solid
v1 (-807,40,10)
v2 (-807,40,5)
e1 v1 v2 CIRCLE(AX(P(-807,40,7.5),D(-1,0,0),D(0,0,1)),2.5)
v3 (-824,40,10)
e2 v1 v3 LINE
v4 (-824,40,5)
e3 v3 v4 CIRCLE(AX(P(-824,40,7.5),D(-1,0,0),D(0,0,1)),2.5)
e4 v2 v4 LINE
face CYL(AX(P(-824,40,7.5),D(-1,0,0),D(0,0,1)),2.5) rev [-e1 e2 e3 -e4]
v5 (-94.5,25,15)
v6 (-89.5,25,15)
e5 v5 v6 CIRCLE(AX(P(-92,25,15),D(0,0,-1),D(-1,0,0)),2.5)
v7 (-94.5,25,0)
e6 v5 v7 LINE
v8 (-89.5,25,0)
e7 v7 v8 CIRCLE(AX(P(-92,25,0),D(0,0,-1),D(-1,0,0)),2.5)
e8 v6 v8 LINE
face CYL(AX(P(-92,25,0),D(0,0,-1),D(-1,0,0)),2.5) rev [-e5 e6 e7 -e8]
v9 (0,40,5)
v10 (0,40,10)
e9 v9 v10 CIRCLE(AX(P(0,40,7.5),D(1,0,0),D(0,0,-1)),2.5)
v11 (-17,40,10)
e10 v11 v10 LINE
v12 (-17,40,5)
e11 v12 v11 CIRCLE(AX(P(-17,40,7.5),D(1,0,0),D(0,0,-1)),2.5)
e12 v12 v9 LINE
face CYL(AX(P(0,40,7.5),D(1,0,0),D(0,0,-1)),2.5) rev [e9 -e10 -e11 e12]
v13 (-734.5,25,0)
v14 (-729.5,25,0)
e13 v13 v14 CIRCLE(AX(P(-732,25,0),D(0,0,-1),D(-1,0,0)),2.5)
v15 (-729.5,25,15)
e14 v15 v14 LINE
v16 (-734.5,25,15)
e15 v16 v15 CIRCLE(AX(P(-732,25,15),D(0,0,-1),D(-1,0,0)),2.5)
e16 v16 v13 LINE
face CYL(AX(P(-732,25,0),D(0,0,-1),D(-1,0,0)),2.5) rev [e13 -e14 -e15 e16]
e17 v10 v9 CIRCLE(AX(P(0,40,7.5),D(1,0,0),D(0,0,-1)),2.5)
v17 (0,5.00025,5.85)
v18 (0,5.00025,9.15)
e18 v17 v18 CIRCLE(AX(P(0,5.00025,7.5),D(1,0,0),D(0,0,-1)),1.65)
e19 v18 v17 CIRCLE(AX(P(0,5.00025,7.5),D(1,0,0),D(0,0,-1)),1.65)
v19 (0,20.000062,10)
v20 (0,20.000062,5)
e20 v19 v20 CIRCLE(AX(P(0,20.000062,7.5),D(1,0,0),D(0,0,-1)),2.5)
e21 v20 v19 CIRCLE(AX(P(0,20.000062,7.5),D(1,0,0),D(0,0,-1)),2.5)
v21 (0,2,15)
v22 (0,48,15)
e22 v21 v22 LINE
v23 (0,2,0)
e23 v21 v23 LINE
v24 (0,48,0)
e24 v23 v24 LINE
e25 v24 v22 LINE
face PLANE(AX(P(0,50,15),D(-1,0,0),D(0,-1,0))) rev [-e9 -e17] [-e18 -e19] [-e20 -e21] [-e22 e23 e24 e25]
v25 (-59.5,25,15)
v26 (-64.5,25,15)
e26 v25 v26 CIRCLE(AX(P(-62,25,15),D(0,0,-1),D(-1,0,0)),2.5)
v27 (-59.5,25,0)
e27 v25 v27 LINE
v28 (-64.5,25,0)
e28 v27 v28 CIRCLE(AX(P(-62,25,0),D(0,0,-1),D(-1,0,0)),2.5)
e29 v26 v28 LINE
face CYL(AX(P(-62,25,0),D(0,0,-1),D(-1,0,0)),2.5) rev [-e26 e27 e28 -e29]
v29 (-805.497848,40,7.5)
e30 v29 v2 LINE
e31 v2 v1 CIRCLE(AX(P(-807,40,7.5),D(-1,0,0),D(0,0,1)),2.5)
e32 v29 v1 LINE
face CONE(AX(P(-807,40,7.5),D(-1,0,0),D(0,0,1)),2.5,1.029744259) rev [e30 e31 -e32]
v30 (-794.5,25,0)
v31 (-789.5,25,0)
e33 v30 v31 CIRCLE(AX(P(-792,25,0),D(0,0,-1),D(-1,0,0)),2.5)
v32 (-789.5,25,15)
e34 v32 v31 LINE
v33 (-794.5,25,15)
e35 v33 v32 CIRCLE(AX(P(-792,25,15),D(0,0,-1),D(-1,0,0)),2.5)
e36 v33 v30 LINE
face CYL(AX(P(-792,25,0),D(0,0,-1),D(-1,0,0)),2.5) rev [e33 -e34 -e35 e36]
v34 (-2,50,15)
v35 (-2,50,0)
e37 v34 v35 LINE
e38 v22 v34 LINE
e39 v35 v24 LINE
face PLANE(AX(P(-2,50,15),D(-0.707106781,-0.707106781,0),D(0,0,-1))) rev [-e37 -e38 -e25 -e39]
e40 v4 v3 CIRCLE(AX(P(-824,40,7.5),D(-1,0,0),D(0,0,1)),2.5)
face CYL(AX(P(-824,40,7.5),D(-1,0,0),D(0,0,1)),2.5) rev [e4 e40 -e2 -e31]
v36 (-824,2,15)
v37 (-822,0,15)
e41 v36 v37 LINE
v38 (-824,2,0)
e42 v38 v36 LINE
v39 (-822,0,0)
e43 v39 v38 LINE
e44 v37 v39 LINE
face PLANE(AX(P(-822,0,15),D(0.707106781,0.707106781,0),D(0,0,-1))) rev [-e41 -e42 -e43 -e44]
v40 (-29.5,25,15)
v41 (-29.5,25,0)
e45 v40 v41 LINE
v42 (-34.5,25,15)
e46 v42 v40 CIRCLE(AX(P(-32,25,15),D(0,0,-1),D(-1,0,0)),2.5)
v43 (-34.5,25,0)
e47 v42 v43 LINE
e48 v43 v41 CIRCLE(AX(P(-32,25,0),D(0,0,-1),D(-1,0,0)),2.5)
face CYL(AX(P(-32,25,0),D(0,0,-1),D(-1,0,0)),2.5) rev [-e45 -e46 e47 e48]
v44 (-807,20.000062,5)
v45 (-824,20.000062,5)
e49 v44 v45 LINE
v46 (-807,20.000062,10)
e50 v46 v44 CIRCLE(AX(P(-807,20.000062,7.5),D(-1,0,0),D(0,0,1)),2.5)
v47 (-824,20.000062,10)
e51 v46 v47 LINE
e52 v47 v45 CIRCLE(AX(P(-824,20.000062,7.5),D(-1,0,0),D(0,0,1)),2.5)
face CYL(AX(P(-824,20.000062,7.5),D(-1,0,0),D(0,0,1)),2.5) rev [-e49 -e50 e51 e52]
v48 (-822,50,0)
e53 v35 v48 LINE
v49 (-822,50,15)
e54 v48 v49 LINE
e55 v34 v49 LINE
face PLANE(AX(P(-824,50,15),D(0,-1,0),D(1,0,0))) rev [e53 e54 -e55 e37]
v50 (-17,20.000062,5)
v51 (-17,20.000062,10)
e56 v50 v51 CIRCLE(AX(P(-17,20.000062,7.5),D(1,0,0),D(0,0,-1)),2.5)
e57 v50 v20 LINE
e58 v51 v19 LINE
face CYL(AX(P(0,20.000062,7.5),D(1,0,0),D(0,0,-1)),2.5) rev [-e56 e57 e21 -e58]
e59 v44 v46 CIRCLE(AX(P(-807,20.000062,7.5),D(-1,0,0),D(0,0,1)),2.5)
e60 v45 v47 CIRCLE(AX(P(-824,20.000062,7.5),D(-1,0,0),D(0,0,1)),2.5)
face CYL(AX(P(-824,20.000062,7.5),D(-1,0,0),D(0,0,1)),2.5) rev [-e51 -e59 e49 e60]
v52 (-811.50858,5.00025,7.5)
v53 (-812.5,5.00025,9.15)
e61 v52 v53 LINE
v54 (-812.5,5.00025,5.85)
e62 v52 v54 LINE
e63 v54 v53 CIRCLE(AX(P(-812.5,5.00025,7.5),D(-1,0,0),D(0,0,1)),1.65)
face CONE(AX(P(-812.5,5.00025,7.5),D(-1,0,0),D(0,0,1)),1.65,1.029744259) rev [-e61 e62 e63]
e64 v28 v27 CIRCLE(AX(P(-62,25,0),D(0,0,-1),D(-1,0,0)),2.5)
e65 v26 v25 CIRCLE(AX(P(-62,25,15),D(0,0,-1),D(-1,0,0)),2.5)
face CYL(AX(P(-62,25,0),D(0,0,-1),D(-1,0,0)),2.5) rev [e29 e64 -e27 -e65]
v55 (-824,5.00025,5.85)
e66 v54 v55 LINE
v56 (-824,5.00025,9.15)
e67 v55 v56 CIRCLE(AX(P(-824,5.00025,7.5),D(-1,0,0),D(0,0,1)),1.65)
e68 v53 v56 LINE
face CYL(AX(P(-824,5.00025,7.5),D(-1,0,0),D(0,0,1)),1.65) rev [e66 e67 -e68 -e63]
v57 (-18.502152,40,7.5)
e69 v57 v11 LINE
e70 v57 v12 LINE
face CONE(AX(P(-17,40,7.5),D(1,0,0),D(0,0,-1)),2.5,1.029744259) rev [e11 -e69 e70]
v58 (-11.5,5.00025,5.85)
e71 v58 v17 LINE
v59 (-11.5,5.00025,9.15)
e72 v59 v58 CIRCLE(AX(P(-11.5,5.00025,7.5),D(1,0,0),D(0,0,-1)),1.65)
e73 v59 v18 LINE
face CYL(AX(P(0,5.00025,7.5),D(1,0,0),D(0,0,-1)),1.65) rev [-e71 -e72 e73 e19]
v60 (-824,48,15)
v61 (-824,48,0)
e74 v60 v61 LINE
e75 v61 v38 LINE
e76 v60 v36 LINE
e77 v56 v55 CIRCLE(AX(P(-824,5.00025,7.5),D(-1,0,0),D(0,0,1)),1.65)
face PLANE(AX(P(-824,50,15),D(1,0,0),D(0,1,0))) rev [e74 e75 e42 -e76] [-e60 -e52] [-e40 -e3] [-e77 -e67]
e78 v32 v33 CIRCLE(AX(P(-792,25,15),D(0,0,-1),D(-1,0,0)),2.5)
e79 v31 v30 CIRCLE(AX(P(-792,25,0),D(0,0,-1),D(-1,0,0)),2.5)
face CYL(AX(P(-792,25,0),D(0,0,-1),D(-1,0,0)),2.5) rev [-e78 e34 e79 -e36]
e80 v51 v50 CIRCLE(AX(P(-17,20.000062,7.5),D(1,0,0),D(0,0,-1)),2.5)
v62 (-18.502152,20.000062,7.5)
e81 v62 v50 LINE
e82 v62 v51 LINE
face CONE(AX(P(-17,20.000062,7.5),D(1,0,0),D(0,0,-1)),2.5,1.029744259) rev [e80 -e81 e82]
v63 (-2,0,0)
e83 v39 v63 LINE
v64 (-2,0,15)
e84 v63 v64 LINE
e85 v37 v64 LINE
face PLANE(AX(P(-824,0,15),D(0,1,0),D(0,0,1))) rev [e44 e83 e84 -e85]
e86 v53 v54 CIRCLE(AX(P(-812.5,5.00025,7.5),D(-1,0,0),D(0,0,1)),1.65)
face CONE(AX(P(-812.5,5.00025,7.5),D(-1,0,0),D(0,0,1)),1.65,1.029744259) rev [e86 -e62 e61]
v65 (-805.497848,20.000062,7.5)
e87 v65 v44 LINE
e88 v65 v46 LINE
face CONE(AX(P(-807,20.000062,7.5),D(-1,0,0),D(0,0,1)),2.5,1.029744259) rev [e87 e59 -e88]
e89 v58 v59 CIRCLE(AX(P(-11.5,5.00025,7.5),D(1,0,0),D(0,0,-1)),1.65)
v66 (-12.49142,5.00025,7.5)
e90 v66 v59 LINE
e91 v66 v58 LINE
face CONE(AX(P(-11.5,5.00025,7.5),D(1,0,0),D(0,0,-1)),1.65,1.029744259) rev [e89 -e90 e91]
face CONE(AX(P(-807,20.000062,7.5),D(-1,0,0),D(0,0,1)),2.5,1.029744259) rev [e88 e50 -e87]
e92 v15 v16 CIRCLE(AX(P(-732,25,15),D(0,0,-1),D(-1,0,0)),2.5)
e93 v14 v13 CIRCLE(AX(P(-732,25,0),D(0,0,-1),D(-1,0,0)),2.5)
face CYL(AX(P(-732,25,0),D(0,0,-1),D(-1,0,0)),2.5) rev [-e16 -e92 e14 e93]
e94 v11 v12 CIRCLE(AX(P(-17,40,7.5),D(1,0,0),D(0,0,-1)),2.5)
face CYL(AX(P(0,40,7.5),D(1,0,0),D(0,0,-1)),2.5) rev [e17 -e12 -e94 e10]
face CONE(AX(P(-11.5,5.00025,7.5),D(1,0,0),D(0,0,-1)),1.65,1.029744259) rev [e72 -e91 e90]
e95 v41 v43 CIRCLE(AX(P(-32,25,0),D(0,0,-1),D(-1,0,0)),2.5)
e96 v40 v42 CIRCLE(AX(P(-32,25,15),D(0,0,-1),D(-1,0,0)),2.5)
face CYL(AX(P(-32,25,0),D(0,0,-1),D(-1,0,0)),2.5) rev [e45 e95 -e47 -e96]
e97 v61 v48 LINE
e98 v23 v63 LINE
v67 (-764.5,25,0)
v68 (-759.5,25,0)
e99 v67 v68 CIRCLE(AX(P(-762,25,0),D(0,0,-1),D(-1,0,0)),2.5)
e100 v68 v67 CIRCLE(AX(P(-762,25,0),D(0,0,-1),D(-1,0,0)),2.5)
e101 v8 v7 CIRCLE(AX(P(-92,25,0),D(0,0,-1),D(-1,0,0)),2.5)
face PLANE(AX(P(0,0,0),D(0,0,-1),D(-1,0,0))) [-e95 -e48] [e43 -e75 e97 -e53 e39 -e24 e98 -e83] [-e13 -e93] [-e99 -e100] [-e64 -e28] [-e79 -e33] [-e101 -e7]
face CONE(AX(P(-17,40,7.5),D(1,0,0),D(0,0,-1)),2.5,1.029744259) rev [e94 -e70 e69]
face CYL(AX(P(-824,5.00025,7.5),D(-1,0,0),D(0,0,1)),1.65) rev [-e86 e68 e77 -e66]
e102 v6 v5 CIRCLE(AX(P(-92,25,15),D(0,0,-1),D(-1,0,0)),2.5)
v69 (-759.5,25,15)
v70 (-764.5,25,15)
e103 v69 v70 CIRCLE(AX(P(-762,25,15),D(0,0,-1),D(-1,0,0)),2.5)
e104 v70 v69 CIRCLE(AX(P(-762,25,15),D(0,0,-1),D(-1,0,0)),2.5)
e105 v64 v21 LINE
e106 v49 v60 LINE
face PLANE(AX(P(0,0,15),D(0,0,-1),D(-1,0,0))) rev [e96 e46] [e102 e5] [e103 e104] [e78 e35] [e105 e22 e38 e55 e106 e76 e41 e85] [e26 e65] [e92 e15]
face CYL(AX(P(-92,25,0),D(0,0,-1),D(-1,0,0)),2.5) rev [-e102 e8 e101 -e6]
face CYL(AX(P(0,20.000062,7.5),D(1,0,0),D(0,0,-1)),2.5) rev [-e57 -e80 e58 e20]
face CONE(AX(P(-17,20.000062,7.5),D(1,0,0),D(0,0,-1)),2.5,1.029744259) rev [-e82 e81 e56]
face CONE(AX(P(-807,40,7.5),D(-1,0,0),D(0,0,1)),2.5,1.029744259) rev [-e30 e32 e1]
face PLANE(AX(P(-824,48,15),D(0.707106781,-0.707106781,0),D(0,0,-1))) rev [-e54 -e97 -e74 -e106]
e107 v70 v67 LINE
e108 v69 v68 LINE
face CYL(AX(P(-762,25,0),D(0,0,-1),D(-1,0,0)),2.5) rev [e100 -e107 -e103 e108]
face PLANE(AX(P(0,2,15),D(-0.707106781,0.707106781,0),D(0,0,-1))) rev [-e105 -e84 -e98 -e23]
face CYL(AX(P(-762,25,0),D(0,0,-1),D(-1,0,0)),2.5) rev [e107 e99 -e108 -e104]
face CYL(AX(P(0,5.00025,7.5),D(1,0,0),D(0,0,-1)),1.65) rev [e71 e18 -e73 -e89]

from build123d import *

# Parameters (mm, degrees)
SKETCH_1_W                  = 824
SKETCH_1_H                  = 50
EXTRUDE_1_DEPTH             = 15
HOLE_WIZARD_M6_1_AT_2_COUNT = 2
HOLE_WIZARD_M6_1_AT_2_PITCH = 19.9999375
HOLE_WIZARD_M6_2_D          = 5
HOLE_WIZARD_M6_2_DEPTH      = 17
HOLE_WIZARD_M6_2_TIP        = 1.502151548
CHAMFER_1_SIZE              = 2


with BuildPart() as part:
    # 草图1 → 凸台-拉伸1 (new body)
    with BuildSketch(Plane.XY):
        with Locations((-412, 25)):
            Rectangle(SKETCH_1_W, SKETCH_1_H)
    extrude(amount=EXTRUDE_1_DEPTH)

    # 草图3 → M6 螺纹孔1 (revolve, cut)
    with BuildSketch(Plane(origin=(0, 40, 7.5), x_dir=(0, 0, -1), z_dir=(0, 1, 0))):
        Polygon((0, 0), (0, 18.502151548), (2.5, 17), (2.5, 0), align=None)
    hole_wizard_m6_1 = revolve(axis=Axis((6.35, 40, 7.5), (-1, 0, 0)), mode=Mode.SUBTRACT)

    # M6 螺纹孔1 at 2: M6 螺纹孔1 ×2
    with Locations(*[(0, -i * HOLE_WIZARD_M6_1_AT_2_PITCH, 0) for i in range(1, HOLE_WIZARD_M6_1_AT_2_COUNT)]):
        add(hole_wizard_m6_1, mode=Mode.SUBTRACT)

    # 草图5 → M4 螺纹孔1 (revolve, cut)
    with BuildSketch(Plane(origin=(0, 5.000249994, 7.5), x_dir=(0, 0, -1), z_dir=(0, 1, 0))):
        Polygon((0, 0), (0, 12.491420021), (1.65, 11.5), (1.65, 0), align=None)
    hole_wizard_m4_1 = revolve(axis=Axis((6.35, 5.000249994, 7.5), (-1, 0, 0)), mode=Mode.SUBTRACT)

    # 镜向1: M6 螺纹孔1, M4 螺纹孔1 across plane
    add(hole_wizard_m6_1.mirror(Plane(origin=(-412, 0, 0), x_dir=(0, 0, 1), z_dir=(1, 0, 0))), mode=Mode.SUBTRACT)
    add(hole_wizard_m4_1.mirror(Plane(origin=(-412, 0, 0), x_dir=(0, 0, 1), z_dir=(1, 0, 0))), mode=Mode.SUBTRACT)

    # 镜向1 copy 1 sketch → 镜向1 copy 1 (revolve, cut)
    with BuildSketch(Plane(origin=(-824, 20.0000625, 7.5), x_dir=(0, 0, -1), z_dir=(0, 1, 0))):
        Polygon((0, 0), (0, -18.502151548), (2.5, -17), (2.5, 0), align=None)
    revolve(axis=Axis((-830.35, 20.0000625, 7.5), (-1, 0, 0)), mode=Mode.SUBTRACT)

    # M6 螺纹孔2
    with Locations(Plane(origin=(0, 0, 0), x_dir=(-1, 0, 0), z_dir=(0, 0, -1))):
        with Locations((792, 25), (32, 25), (62, 25), (92, 25), (732, 25), (762, 25)):
            Hole(HOLE_WIZARD_M6_2_D / 2, depth=HOLE_WIZARD_M6_2_DEPTH)
            with Locations((0, 0, -(HOLE_WIZARD_M6_2_DEPTH + HOLE_WIZARD_M6_2_TIP / 2))):  # 118° drill point
                Cone(0, HOLE_WIZARD_M6_2_D / 2, HOLE_WIZARD_M6_2_TIP, mode=Mode.SUBTRACT)

    # 倒角1
    chamfer_1_edges = [part.edges().sort_by_distance(p)[0] for p in [
        (0, 50, 7.5),
        (0, 0, 7.5),
        (-824, 0, 7.5),
        (-824, 50, 7.5),
    ]]
    chamfer(chamfer_1_edges, length=CHAMFER_1_SIZE)


solid = part.part
